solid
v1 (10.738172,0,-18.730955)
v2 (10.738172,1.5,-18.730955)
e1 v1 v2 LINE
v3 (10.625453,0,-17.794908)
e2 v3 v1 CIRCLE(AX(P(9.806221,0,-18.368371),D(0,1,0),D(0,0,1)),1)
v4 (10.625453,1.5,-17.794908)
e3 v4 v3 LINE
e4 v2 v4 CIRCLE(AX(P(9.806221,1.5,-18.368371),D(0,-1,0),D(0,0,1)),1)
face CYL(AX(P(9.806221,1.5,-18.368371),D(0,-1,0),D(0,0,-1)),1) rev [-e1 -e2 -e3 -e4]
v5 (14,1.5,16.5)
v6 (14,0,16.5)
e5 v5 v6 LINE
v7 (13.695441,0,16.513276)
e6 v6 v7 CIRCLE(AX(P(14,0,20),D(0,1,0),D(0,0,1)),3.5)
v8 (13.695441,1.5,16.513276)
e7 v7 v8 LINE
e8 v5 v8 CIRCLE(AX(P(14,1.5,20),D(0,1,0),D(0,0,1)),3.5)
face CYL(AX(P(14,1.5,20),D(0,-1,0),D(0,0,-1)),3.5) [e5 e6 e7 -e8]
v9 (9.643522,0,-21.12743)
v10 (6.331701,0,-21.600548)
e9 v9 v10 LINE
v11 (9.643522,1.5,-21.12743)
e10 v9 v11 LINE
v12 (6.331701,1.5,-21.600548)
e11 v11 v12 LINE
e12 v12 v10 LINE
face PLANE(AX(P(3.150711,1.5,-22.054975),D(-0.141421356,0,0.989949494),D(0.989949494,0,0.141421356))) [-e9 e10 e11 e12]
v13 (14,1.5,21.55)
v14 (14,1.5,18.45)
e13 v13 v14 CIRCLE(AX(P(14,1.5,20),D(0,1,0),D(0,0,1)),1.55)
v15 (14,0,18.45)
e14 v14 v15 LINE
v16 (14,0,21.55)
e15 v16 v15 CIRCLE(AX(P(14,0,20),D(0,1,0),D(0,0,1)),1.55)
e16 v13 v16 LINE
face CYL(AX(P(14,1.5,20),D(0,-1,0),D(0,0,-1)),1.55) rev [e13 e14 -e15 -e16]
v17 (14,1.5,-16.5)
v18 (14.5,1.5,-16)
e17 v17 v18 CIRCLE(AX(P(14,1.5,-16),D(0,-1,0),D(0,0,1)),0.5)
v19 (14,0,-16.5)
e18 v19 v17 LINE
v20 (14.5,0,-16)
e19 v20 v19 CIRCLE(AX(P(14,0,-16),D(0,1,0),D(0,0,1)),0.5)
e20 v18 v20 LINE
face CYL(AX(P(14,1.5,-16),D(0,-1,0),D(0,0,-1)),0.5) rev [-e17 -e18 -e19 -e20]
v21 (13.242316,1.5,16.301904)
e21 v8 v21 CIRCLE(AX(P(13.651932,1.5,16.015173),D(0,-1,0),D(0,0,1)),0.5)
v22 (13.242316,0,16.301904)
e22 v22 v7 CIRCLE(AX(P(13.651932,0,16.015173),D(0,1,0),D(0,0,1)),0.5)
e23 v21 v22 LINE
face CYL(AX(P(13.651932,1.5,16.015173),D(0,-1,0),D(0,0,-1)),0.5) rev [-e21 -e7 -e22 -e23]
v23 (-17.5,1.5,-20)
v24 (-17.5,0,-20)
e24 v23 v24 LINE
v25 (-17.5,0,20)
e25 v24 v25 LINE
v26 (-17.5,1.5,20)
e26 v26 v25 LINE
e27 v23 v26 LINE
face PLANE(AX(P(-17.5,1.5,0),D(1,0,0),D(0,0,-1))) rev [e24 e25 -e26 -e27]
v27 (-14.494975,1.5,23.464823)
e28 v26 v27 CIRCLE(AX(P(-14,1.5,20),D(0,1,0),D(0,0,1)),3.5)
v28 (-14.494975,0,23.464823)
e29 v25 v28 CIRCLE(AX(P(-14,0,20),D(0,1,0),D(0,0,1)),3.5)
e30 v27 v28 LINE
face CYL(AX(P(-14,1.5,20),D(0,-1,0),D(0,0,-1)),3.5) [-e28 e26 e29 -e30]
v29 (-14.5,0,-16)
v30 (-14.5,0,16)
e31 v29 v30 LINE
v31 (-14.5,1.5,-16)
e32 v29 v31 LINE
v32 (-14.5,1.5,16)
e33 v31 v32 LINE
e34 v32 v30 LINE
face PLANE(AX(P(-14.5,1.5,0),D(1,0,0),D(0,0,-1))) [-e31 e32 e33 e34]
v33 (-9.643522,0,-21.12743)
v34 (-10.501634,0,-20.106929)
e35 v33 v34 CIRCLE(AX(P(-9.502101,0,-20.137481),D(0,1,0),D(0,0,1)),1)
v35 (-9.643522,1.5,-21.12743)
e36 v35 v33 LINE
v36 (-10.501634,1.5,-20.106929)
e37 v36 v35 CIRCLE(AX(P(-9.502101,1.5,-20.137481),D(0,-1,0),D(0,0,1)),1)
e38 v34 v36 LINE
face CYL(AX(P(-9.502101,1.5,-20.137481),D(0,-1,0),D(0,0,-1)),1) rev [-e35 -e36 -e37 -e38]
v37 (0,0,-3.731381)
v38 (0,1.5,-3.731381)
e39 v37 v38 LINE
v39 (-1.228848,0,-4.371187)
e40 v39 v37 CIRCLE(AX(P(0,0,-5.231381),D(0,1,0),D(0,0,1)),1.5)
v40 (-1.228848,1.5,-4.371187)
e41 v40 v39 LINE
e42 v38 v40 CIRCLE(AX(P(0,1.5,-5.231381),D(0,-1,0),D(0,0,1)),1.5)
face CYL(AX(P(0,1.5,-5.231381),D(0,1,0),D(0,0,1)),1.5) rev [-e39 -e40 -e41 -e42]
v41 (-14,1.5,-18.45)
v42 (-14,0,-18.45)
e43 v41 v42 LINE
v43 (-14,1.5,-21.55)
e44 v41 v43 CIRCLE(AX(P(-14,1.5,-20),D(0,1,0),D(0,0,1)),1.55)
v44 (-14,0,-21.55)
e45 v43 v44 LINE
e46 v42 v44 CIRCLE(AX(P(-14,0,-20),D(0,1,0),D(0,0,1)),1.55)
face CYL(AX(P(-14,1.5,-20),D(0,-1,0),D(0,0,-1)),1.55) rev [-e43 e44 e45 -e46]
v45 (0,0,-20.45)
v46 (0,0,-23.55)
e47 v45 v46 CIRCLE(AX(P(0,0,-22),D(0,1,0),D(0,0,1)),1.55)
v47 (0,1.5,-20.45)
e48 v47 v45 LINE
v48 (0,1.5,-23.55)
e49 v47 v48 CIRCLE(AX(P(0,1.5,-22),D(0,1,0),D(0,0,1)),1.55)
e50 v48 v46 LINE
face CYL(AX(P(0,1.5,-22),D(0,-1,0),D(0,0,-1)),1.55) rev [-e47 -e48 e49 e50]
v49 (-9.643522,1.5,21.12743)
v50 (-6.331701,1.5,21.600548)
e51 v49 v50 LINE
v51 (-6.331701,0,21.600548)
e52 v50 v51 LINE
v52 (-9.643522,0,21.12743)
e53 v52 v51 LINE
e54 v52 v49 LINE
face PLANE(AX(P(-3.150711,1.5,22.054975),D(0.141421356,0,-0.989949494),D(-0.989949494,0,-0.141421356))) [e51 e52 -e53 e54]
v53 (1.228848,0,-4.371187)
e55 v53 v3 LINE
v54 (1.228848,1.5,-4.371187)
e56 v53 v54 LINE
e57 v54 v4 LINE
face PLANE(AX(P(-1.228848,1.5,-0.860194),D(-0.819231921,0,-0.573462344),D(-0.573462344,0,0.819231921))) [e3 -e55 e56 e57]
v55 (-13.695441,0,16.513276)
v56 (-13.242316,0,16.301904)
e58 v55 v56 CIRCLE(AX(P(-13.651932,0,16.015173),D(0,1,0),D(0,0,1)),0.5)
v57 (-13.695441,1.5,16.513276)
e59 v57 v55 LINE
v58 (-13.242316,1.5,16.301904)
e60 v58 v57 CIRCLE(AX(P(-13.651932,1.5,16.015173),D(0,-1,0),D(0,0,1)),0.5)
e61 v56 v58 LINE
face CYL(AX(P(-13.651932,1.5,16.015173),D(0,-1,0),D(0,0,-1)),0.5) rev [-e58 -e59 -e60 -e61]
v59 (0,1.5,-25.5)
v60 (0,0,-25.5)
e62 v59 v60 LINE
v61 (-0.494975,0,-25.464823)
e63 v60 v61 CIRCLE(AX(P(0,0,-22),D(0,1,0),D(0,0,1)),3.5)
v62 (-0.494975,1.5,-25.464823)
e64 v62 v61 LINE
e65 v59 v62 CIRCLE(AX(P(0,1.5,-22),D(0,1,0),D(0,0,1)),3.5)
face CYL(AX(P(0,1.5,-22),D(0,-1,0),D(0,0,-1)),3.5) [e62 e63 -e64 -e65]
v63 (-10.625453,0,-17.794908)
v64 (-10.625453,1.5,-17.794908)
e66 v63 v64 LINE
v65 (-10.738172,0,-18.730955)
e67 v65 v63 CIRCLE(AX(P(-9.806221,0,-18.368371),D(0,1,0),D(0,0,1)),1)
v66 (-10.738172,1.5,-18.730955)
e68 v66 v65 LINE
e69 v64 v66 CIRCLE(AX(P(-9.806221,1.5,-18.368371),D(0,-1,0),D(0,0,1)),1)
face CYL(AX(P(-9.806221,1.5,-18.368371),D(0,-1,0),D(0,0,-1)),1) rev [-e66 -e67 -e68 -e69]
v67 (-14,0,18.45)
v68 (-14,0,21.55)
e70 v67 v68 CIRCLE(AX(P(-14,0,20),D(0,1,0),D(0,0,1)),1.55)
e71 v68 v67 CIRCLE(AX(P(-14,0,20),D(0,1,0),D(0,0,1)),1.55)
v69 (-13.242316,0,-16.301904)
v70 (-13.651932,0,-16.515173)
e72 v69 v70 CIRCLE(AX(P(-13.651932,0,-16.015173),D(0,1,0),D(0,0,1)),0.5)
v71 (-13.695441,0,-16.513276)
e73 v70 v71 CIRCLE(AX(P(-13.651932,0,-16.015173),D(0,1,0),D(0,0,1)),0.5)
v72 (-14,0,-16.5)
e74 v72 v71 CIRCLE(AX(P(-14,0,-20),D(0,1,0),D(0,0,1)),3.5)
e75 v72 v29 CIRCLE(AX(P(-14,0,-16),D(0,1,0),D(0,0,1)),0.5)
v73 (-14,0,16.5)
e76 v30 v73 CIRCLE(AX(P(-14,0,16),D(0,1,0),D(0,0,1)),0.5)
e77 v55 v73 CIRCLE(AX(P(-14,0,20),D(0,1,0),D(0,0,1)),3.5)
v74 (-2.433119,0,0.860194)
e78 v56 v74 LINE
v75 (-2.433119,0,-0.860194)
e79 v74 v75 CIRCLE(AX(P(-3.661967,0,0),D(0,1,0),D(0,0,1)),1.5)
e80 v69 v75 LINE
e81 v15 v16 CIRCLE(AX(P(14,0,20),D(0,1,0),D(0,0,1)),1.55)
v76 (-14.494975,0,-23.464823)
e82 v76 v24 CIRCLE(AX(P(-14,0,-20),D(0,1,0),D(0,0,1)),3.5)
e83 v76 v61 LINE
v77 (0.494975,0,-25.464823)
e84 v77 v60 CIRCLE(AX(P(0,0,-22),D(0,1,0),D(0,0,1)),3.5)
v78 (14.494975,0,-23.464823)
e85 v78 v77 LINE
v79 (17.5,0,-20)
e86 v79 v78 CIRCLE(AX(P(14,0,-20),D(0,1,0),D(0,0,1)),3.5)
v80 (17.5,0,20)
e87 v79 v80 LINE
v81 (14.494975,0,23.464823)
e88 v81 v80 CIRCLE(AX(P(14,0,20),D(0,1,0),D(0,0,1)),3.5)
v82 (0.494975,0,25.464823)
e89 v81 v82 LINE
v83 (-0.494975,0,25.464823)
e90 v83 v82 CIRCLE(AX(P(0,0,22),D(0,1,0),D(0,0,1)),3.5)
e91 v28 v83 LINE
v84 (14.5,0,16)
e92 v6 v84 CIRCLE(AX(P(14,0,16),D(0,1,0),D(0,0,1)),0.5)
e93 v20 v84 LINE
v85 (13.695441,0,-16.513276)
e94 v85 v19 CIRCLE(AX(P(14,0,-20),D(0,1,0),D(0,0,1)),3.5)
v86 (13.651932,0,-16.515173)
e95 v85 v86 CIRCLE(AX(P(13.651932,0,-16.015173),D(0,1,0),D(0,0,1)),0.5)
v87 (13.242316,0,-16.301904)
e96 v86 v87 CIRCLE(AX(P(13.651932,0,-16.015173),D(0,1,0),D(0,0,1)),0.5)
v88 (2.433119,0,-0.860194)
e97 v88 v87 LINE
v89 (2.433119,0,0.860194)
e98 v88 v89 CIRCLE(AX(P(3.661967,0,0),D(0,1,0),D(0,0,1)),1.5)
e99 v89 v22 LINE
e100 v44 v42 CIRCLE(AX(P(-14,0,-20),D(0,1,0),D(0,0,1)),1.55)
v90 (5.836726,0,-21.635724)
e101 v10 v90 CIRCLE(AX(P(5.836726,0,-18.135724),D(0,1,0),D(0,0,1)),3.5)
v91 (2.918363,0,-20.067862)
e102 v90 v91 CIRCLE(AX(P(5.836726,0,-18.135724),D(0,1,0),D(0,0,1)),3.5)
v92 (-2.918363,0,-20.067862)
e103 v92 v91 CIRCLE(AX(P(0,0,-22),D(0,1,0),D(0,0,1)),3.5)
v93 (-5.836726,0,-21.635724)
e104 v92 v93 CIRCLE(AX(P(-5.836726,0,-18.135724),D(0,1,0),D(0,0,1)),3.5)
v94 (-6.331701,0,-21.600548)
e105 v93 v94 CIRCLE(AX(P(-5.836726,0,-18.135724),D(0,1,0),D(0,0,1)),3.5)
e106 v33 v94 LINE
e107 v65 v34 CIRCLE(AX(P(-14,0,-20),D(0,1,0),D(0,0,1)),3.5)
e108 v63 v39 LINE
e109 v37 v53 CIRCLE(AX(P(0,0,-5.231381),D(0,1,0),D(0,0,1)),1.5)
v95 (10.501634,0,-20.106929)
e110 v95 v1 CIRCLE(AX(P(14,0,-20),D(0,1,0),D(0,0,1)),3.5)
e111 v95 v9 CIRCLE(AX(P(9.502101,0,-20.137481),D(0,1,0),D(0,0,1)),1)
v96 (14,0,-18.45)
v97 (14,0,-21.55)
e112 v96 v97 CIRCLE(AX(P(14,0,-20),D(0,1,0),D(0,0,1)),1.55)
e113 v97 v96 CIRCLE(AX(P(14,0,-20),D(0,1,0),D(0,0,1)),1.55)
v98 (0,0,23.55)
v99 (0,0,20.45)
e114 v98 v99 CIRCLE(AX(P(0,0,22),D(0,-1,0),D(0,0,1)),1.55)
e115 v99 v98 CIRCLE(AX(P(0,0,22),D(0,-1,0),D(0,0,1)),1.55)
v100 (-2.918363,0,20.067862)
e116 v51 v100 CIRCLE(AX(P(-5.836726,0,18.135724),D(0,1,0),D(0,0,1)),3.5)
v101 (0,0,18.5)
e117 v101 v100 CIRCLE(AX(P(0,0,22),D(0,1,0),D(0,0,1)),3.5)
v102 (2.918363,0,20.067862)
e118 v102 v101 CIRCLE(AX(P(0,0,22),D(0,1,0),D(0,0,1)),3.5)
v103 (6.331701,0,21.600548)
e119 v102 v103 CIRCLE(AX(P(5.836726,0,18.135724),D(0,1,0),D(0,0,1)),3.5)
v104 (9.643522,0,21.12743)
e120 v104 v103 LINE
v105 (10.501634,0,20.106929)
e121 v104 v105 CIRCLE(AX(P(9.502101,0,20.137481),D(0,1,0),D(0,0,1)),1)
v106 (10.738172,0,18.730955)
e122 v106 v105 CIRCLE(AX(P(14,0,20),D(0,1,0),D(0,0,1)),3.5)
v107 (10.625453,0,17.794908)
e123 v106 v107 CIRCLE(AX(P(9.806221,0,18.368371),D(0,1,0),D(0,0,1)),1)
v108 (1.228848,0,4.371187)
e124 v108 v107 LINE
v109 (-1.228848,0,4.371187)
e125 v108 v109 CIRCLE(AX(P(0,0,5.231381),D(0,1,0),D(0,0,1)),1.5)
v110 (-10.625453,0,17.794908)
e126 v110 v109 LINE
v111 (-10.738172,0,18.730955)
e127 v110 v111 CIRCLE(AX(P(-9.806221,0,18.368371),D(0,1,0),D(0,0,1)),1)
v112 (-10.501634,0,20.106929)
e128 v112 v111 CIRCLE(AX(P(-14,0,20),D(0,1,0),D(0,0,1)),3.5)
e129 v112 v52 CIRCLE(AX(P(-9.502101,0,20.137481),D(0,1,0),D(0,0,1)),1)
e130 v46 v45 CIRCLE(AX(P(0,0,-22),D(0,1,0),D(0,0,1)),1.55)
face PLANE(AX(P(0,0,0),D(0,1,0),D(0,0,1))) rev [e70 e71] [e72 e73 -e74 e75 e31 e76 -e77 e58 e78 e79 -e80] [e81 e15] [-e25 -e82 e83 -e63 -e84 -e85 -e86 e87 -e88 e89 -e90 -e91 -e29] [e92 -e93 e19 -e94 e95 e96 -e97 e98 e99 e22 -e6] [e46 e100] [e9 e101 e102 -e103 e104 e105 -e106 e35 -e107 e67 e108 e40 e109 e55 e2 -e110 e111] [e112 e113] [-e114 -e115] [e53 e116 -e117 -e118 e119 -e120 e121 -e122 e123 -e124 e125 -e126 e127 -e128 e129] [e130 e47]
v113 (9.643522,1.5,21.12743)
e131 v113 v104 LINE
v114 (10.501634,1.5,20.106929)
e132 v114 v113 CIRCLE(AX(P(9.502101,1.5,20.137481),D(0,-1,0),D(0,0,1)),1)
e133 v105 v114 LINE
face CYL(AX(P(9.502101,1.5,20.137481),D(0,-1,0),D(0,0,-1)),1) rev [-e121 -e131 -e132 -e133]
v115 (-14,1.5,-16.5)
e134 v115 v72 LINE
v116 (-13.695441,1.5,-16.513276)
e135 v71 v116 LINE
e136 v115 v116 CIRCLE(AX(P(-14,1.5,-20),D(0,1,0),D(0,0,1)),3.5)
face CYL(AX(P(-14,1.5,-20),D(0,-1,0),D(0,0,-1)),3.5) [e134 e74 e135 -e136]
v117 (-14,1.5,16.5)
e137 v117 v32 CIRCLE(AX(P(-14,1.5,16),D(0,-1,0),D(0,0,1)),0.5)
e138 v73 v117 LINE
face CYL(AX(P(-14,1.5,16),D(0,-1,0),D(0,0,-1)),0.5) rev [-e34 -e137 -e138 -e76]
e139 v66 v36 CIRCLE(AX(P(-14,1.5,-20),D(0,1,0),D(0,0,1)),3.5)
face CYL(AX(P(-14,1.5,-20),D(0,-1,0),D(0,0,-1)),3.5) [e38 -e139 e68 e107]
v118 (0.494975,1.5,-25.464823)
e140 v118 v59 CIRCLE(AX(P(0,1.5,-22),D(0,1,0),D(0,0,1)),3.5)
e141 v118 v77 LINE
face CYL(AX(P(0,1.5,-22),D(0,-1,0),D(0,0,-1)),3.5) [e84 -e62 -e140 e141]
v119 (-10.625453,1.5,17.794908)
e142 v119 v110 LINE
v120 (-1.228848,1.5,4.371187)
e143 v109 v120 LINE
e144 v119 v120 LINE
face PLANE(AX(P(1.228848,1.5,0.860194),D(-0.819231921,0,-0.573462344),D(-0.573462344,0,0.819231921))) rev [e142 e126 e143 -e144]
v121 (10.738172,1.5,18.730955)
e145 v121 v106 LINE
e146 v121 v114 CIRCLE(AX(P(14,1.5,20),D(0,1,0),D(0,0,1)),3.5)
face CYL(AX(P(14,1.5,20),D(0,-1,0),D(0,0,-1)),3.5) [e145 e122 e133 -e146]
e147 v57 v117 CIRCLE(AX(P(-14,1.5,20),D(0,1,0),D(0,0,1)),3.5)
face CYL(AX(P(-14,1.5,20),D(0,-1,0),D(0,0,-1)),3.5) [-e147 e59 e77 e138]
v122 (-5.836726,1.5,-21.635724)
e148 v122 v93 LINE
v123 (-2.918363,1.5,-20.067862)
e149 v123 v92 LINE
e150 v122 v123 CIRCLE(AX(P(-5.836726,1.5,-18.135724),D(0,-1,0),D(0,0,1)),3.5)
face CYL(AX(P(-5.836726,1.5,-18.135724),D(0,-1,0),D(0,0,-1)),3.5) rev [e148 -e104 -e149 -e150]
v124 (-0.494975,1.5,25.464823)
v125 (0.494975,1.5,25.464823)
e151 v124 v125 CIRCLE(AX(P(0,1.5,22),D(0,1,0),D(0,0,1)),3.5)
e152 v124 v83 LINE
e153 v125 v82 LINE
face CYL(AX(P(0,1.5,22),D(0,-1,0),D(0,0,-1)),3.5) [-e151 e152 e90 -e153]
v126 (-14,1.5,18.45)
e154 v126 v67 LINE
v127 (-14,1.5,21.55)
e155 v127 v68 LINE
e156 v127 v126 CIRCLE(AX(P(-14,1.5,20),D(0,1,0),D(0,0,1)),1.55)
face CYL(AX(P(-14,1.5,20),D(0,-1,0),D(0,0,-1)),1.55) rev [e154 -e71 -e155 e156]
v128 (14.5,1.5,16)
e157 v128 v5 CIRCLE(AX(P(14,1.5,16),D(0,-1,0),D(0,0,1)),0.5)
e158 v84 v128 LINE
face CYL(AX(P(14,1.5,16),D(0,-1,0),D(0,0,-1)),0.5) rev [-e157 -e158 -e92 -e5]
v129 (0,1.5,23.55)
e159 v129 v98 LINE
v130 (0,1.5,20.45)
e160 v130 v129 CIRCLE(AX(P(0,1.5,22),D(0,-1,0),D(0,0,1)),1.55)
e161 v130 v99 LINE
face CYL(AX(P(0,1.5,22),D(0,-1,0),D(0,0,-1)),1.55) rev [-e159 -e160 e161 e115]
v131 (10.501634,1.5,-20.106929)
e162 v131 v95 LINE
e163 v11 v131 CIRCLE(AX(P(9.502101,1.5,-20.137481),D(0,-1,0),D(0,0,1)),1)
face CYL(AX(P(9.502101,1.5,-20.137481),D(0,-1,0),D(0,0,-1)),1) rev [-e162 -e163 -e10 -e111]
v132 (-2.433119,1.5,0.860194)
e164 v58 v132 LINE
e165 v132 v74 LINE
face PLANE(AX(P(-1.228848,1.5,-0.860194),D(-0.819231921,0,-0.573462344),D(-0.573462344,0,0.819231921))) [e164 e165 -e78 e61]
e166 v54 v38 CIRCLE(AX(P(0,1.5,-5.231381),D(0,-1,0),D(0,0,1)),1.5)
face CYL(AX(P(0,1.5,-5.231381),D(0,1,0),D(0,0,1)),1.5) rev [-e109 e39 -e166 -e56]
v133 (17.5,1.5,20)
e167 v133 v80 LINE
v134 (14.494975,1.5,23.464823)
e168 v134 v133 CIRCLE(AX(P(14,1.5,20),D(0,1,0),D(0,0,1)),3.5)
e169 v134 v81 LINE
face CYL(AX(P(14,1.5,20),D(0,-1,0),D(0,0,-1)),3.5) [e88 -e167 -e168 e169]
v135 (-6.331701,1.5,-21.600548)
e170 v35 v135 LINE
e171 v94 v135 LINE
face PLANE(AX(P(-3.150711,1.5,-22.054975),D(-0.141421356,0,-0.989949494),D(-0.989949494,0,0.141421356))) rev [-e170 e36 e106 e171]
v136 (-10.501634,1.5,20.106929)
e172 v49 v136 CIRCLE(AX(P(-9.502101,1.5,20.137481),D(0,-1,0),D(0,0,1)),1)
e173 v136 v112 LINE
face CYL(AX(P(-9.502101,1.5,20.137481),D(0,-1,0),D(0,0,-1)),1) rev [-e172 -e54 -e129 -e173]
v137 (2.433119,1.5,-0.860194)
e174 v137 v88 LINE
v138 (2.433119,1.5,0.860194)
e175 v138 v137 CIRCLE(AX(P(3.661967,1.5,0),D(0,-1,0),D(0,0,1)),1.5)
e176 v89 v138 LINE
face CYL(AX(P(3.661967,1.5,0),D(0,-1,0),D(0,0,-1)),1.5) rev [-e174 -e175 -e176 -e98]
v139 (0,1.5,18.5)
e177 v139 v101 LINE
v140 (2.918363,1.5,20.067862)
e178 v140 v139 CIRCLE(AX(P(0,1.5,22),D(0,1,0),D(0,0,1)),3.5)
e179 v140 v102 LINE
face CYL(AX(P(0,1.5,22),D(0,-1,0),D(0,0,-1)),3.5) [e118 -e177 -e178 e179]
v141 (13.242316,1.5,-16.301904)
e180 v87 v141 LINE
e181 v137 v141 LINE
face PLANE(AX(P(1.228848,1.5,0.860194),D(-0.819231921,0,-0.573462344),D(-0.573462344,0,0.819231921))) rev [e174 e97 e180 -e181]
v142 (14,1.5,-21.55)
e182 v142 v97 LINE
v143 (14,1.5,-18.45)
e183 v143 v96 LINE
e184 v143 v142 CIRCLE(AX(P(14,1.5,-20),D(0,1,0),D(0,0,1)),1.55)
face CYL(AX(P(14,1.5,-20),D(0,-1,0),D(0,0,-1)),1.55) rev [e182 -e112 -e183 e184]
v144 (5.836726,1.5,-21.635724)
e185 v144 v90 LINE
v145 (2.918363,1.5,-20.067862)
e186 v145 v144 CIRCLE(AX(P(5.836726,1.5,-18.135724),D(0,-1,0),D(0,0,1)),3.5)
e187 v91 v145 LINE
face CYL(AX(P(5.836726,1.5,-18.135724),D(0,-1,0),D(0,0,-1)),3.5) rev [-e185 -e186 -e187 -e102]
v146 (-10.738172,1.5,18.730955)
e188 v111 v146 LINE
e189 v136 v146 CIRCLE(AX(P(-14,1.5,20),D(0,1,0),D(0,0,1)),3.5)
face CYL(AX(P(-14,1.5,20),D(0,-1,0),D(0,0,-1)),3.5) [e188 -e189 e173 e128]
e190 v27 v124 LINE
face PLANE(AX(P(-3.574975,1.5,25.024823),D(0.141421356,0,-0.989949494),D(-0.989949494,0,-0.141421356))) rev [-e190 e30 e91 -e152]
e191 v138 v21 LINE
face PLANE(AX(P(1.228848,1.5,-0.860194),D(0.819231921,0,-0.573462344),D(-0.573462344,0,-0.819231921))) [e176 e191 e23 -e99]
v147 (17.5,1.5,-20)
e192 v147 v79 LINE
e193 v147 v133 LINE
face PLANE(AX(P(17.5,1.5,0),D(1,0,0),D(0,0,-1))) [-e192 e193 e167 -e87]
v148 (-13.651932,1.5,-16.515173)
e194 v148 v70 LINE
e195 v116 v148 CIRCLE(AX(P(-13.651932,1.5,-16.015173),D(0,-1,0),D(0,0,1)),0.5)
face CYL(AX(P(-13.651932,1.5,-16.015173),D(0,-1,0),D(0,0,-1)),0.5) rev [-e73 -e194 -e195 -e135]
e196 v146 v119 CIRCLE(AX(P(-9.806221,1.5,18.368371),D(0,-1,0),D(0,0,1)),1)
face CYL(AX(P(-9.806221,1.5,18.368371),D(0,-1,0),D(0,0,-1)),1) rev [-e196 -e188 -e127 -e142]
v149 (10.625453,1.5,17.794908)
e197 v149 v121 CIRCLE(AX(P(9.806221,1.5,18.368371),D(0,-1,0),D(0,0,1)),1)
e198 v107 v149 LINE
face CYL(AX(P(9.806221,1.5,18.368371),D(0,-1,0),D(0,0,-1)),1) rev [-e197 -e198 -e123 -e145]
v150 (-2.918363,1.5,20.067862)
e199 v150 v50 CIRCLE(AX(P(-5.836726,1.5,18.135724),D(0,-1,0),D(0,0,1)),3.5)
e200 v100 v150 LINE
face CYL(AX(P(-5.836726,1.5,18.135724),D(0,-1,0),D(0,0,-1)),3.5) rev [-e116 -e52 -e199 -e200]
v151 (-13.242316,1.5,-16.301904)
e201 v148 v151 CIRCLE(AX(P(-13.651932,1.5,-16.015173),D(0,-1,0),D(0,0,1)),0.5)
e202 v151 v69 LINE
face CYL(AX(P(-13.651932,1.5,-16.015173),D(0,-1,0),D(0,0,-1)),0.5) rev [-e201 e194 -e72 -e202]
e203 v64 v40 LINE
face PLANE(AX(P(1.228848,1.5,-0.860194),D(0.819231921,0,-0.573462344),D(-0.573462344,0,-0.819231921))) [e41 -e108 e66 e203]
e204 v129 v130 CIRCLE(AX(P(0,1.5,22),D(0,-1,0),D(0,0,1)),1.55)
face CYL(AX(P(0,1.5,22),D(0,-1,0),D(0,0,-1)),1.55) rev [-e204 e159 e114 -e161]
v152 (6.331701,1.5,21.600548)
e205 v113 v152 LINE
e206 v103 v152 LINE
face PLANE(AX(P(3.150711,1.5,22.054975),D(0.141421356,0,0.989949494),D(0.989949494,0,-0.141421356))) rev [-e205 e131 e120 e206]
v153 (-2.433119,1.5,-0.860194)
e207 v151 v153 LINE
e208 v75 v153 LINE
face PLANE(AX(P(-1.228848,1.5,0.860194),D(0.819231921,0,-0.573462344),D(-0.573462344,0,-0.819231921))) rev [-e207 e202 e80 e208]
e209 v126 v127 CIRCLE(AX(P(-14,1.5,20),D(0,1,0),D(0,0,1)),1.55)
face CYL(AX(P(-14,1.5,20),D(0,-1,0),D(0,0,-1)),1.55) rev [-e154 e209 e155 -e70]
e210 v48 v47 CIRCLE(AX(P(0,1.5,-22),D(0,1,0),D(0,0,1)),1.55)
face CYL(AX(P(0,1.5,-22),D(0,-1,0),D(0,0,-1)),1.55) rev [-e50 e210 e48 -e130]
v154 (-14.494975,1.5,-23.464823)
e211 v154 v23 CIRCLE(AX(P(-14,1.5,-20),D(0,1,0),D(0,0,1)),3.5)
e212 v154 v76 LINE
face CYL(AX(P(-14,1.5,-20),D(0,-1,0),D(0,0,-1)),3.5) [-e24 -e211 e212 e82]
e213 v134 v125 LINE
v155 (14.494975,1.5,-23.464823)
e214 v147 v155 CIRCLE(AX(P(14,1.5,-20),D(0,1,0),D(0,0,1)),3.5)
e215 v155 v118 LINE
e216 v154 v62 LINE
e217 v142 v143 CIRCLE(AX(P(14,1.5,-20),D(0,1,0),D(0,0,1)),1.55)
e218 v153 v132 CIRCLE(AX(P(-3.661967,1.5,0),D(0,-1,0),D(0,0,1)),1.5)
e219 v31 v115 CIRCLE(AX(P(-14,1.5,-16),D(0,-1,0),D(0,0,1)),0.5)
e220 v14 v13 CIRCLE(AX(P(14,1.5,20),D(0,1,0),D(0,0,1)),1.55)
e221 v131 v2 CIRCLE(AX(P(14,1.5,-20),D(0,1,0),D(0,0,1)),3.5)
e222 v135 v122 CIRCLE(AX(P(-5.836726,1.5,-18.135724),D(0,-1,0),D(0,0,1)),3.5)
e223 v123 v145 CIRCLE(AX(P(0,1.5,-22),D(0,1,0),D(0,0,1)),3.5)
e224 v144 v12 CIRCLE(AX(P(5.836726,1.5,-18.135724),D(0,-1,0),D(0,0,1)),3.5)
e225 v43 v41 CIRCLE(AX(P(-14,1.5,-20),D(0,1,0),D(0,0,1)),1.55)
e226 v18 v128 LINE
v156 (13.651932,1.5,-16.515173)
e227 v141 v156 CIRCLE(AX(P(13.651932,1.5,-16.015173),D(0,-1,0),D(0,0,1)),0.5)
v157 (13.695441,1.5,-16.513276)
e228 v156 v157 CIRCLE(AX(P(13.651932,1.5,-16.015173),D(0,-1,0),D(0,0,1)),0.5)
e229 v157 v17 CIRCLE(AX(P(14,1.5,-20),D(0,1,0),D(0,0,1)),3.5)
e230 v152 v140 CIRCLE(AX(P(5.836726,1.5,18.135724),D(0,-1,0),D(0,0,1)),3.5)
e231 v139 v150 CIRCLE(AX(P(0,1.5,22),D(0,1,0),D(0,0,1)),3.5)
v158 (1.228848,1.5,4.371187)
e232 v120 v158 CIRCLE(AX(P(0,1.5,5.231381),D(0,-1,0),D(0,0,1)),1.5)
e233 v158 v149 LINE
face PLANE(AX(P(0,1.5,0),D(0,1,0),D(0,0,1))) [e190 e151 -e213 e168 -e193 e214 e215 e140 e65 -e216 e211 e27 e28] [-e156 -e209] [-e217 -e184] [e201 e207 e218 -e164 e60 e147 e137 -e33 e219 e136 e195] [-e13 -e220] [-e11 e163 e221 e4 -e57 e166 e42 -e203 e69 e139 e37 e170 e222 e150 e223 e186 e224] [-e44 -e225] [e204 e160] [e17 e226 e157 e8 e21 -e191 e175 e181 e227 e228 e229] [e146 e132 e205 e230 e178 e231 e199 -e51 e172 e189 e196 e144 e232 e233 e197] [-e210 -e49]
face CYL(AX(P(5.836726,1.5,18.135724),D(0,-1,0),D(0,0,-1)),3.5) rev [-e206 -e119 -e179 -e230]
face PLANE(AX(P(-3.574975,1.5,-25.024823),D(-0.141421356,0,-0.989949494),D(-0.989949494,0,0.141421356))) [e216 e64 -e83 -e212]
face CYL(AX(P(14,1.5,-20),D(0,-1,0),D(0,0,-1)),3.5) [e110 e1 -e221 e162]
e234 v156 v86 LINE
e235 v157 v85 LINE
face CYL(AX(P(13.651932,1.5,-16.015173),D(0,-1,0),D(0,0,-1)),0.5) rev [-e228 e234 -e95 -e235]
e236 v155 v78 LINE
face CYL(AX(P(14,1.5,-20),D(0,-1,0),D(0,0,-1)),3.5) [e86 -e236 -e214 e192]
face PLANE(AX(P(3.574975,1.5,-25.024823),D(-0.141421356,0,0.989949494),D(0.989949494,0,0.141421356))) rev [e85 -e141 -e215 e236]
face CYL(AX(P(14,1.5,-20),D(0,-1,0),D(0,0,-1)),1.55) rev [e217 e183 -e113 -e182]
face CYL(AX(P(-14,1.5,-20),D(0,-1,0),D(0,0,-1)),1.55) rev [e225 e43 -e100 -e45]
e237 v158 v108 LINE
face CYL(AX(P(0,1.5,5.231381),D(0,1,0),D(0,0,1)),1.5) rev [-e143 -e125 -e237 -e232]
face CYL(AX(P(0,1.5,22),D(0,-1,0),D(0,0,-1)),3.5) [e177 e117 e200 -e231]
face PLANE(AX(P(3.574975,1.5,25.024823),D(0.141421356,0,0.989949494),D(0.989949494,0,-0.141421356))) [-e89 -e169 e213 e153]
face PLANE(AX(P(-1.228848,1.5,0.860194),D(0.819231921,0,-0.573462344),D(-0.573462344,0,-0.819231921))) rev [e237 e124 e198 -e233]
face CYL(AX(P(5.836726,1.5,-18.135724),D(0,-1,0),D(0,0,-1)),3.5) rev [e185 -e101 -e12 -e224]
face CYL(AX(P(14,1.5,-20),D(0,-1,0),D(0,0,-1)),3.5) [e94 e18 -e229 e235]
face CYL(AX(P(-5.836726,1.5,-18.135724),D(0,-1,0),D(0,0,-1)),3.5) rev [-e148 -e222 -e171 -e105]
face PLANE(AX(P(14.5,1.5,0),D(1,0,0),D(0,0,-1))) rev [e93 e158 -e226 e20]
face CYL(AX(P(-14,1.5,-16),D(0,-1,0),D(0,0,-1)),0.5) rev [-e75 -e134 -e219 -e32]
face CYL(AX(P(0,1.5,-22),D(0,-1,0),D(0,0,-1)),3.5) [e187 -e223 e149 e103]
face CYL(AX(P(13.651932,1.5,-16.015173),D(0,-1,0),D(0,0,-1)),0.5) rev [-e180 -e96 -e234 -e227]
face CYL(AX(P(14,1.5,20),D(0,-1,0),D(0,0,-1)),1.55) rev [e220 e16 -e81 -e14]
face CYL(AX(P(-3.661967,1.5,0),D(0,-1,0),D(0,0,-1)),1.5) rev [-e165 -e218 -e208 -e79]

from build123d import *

# Parameters (mm, degrees)
SKETCH_1_R      = 1.55
EXTRUDE_1_DEPTH = 1.5
FILLET_1_R      = 0.5
FILLET_2_R      = 1
FILLET_3_R      = 1.5
FILLET_4_R      = 3.5


with BuildPart() as part:
    # 草图1 → 凸台-拉伸1 (new body)
    with BuildSketch(Plane(origin=(0, 0, 0), x_dir=(1, 0, 0), z_dir=(0, 1, 0))):
        with BuildLine():
            ThreePointArc((14.494974747, -23.464823228), (16.644088842, -22.293206095), (17.5, -20))
            Line((17.5, -20), (17.5, 20))
            ThreePointArc((17.5, 20), (16.644088842, 22.293206095), (14.494974747, 23.464823228))
            Line((14.494974747, 23.464823228), (0.494974747, 25.464823228))
            ThreePointArc((0.494974747, 25.464823228), (0, 25.5), (-0.494974747, 25.464823228))
            Line((-0.494974747, 25.464823228), (-14.494974747, 23.464823228))
            ThreePointArc((-14.494974747, 23.464823228), (-16.644088842, 22.293206095), (-17.5, 20))
            Line((-17.5, 20), (-17.5, -20))
            ThreePointArc((-17.5, -20), (-16.644088842, -22.293206095), (-14.494974747, -23.464823228))
            Line((-14.494974747, -23.464823228), (-0.494974747, -25.464823228))
            ThreePointArc((-0.494974747, -25.464823228), (0, -25.5), (0.494974747, -25.464823228))
            Line((0.494974747, -25.464823228), (14.494974747, -23.464823228))
        make_face()
        with BuildLine():
            Line((-10.957704959, -18.269554716), (0, -2.615690489))
            Line((0, -2.615690489), (10.957704959, -18.269554716))
            ThreePointArc((10.957704959, -18.269554716), (10.523504332, -19.595058191), (10.641425038, -20.984872695))
            Line((10.641425038, -20.984872695), (3.499996318, -22.005076798))
            ThreePointArc((3.499996318, -22.005076798), (0, -18.5), (-3.499996318, -22.005076798))
            Line((-3.499996318, -22.005076798), (-10.641425038, -20.984872695))
            ThreePointArc((-10.641425038, -20.984872695), (-10.523504332, -19.595058191), (-10.957704959, -18.269554716))
        make_face(mode=Mode.SUBTRACT)
        with BuildLine():
            ThreePointArc((14.5, -16.535898385), (13.957183203, -16.500261907), (13.41540072, -16.549167683))
            Line((13.41540072, -16.549167683), (1.830983342, 0))
            Line((1.830983342, 0), (13.41540072, 16.549167683))
            ThreePointArc((13.41540072, 16.549167683), (13.957183203, 16.500261907), (14.5, 16.535898385))
            Line((14.5, 16.535898385), (14.5, -16.535898385))
        make_face(mode=Mode.SUBTRACT)
        with BuildLine():
            Line((10.957704959, 18.269554716), (0, 2.615690489))
            Line((0, 2.615690489), (-10.957704959, 18.269554716))
            ThreePointArc((-10.957704959, 18.269554716), (-10.523504332, 19.595058191), (-10.641425038, 20.984872695))
            Line((-10.641425038, 20.984872695), (-3.499996318, 22.005076798))
            ThreePointArc((-3.499996318, 22.005076798), (0, 18.5), (3.499996318, 22.005076798))
            Line((3.499996318, 22.005076798), (10.641425038, 20.984872695))
            ThreePointArc((10.641425038, 20.984872695), (10.523504332, 19.595058191), (10.957704959, 18.269554716))
        make_face(mode=Mode.SUBTRACT)
        with Locations(Location((-14, -20, 0), (0, 0, 270))):
            Circle(SKETCH_1_R, mode=Mode.SUBTRACT)
        with BuildLine():
            Line((-1.830983342, 0), (-13.41540072, -16.549167683))
            ThreePointArc((-13.41540072, -16.549167683), (-13.957183203, -16.500261907), (-14.5, -16.535898385))
            Line((-14.5, -16.535898385), (-14.5, 16.535898385))
            ThreePointArc((-14.5, 16.535898385), (-13.957183203, 16.500261907), (-13.41540072, 16.549167683))
            Line((-13.41540072, 16.549167683), (-1.830983342, 0))
        make_face(mode=Mode.SUBTRACT)
        with Locations(Location((-14, 20, 0), (0, 0, 270))):
            Circle(SKETCH_1_R, mode=Mode.SUBTRACT)
        with Locations(Location((0, 22, 0), (0, 0, 270))):
            Circle(SKETCH_1_R, mode=Mode.SUBTRACT)
        with Locations(Location((0, -22, 0), (0, 0, 270))):
            Circle(SKETCH_1_R, mode=Mode.SUBTRACT)
        with Locations(Location((14, -20, 0), (0, 0, 270))):
            Circle(SKETCH_1_R, mode=Mode.SUBTRACT)
        with Locations(Location((14, 20, 0), (0, 0, 270))):
            Circle(SKETCH_1_R, mode=Mode.SUBTRACT)
    extrude(amount=EXTRUDE_1_DEPTH)

    # 圆角1
    fillet_1_edges = [part.edges().sort_by_distance(p)[0] for p in [
        (-14.5, 0.75, -16.535898385),
        (-14.5, 0.75, 16.535898385),
        (-13.41540072, 0.75, 16.549167683),
        (-13.41540072, 0.75, -16.549167683),
        (13.41540072, 0.75, 16.549167683),
        (14.5, 0.75, 16.535898385),
        (14.5, 0.75, -16.535898385),
        (13.41540072, 0.75, -16.549167683),
    ]]
    fillet(fillet_1_edges, radius=FILLET_1_R)

    # 圆角2
    fillet_2_edges = [part.edges().sort_by_distance(p)[0] for p in [
        (-10.957704959, 0.75, 18.269554716),
        (-10.641425038, 0.75, 20.984872695),
        (10.641425038, 0.75, 20.984872695),
        (10.957704959, 0.75, 18.269554716),
        (-10.641425038, 0.75, -20.984872695),
        (-10.957704959, 0.75, -18.269554716),
        (10.957704959, 0.75, -18.269554716),
        (10.641425038, 0.75, -20.984872695),
    ]]
    fillet(fillet_2_edges, radius=FILLET_2_R)

    # 圆角3
    fillet_3_edges = [part.edges().sort_by_distance(p)[0] for p in [
        (-1.830983342, 0.75, 0),
        (0, 0.75, 2.615690489),
        (1.830983342, 0.75, 0),
        (0, 0.75, -2.615690489),
    ]]
    fillet(fillet_3_edges, radius=FILLET_3_R)

    # 圆角4
    fillet_4_edges = [part.edges().sort_by_distance(p)[0] for p in [
        (-3.499996318, 0.75, 22.005076798),
        (3.499996318, 0.75, 22.005076798),
        (3.499996318, 0.75, -22.005076798),
        (-3.499996318, 0.75, -22.005076798),
    ]]
    fillet(fillet_4_edges, radius=FILLET_4_R)


solid = part.part
